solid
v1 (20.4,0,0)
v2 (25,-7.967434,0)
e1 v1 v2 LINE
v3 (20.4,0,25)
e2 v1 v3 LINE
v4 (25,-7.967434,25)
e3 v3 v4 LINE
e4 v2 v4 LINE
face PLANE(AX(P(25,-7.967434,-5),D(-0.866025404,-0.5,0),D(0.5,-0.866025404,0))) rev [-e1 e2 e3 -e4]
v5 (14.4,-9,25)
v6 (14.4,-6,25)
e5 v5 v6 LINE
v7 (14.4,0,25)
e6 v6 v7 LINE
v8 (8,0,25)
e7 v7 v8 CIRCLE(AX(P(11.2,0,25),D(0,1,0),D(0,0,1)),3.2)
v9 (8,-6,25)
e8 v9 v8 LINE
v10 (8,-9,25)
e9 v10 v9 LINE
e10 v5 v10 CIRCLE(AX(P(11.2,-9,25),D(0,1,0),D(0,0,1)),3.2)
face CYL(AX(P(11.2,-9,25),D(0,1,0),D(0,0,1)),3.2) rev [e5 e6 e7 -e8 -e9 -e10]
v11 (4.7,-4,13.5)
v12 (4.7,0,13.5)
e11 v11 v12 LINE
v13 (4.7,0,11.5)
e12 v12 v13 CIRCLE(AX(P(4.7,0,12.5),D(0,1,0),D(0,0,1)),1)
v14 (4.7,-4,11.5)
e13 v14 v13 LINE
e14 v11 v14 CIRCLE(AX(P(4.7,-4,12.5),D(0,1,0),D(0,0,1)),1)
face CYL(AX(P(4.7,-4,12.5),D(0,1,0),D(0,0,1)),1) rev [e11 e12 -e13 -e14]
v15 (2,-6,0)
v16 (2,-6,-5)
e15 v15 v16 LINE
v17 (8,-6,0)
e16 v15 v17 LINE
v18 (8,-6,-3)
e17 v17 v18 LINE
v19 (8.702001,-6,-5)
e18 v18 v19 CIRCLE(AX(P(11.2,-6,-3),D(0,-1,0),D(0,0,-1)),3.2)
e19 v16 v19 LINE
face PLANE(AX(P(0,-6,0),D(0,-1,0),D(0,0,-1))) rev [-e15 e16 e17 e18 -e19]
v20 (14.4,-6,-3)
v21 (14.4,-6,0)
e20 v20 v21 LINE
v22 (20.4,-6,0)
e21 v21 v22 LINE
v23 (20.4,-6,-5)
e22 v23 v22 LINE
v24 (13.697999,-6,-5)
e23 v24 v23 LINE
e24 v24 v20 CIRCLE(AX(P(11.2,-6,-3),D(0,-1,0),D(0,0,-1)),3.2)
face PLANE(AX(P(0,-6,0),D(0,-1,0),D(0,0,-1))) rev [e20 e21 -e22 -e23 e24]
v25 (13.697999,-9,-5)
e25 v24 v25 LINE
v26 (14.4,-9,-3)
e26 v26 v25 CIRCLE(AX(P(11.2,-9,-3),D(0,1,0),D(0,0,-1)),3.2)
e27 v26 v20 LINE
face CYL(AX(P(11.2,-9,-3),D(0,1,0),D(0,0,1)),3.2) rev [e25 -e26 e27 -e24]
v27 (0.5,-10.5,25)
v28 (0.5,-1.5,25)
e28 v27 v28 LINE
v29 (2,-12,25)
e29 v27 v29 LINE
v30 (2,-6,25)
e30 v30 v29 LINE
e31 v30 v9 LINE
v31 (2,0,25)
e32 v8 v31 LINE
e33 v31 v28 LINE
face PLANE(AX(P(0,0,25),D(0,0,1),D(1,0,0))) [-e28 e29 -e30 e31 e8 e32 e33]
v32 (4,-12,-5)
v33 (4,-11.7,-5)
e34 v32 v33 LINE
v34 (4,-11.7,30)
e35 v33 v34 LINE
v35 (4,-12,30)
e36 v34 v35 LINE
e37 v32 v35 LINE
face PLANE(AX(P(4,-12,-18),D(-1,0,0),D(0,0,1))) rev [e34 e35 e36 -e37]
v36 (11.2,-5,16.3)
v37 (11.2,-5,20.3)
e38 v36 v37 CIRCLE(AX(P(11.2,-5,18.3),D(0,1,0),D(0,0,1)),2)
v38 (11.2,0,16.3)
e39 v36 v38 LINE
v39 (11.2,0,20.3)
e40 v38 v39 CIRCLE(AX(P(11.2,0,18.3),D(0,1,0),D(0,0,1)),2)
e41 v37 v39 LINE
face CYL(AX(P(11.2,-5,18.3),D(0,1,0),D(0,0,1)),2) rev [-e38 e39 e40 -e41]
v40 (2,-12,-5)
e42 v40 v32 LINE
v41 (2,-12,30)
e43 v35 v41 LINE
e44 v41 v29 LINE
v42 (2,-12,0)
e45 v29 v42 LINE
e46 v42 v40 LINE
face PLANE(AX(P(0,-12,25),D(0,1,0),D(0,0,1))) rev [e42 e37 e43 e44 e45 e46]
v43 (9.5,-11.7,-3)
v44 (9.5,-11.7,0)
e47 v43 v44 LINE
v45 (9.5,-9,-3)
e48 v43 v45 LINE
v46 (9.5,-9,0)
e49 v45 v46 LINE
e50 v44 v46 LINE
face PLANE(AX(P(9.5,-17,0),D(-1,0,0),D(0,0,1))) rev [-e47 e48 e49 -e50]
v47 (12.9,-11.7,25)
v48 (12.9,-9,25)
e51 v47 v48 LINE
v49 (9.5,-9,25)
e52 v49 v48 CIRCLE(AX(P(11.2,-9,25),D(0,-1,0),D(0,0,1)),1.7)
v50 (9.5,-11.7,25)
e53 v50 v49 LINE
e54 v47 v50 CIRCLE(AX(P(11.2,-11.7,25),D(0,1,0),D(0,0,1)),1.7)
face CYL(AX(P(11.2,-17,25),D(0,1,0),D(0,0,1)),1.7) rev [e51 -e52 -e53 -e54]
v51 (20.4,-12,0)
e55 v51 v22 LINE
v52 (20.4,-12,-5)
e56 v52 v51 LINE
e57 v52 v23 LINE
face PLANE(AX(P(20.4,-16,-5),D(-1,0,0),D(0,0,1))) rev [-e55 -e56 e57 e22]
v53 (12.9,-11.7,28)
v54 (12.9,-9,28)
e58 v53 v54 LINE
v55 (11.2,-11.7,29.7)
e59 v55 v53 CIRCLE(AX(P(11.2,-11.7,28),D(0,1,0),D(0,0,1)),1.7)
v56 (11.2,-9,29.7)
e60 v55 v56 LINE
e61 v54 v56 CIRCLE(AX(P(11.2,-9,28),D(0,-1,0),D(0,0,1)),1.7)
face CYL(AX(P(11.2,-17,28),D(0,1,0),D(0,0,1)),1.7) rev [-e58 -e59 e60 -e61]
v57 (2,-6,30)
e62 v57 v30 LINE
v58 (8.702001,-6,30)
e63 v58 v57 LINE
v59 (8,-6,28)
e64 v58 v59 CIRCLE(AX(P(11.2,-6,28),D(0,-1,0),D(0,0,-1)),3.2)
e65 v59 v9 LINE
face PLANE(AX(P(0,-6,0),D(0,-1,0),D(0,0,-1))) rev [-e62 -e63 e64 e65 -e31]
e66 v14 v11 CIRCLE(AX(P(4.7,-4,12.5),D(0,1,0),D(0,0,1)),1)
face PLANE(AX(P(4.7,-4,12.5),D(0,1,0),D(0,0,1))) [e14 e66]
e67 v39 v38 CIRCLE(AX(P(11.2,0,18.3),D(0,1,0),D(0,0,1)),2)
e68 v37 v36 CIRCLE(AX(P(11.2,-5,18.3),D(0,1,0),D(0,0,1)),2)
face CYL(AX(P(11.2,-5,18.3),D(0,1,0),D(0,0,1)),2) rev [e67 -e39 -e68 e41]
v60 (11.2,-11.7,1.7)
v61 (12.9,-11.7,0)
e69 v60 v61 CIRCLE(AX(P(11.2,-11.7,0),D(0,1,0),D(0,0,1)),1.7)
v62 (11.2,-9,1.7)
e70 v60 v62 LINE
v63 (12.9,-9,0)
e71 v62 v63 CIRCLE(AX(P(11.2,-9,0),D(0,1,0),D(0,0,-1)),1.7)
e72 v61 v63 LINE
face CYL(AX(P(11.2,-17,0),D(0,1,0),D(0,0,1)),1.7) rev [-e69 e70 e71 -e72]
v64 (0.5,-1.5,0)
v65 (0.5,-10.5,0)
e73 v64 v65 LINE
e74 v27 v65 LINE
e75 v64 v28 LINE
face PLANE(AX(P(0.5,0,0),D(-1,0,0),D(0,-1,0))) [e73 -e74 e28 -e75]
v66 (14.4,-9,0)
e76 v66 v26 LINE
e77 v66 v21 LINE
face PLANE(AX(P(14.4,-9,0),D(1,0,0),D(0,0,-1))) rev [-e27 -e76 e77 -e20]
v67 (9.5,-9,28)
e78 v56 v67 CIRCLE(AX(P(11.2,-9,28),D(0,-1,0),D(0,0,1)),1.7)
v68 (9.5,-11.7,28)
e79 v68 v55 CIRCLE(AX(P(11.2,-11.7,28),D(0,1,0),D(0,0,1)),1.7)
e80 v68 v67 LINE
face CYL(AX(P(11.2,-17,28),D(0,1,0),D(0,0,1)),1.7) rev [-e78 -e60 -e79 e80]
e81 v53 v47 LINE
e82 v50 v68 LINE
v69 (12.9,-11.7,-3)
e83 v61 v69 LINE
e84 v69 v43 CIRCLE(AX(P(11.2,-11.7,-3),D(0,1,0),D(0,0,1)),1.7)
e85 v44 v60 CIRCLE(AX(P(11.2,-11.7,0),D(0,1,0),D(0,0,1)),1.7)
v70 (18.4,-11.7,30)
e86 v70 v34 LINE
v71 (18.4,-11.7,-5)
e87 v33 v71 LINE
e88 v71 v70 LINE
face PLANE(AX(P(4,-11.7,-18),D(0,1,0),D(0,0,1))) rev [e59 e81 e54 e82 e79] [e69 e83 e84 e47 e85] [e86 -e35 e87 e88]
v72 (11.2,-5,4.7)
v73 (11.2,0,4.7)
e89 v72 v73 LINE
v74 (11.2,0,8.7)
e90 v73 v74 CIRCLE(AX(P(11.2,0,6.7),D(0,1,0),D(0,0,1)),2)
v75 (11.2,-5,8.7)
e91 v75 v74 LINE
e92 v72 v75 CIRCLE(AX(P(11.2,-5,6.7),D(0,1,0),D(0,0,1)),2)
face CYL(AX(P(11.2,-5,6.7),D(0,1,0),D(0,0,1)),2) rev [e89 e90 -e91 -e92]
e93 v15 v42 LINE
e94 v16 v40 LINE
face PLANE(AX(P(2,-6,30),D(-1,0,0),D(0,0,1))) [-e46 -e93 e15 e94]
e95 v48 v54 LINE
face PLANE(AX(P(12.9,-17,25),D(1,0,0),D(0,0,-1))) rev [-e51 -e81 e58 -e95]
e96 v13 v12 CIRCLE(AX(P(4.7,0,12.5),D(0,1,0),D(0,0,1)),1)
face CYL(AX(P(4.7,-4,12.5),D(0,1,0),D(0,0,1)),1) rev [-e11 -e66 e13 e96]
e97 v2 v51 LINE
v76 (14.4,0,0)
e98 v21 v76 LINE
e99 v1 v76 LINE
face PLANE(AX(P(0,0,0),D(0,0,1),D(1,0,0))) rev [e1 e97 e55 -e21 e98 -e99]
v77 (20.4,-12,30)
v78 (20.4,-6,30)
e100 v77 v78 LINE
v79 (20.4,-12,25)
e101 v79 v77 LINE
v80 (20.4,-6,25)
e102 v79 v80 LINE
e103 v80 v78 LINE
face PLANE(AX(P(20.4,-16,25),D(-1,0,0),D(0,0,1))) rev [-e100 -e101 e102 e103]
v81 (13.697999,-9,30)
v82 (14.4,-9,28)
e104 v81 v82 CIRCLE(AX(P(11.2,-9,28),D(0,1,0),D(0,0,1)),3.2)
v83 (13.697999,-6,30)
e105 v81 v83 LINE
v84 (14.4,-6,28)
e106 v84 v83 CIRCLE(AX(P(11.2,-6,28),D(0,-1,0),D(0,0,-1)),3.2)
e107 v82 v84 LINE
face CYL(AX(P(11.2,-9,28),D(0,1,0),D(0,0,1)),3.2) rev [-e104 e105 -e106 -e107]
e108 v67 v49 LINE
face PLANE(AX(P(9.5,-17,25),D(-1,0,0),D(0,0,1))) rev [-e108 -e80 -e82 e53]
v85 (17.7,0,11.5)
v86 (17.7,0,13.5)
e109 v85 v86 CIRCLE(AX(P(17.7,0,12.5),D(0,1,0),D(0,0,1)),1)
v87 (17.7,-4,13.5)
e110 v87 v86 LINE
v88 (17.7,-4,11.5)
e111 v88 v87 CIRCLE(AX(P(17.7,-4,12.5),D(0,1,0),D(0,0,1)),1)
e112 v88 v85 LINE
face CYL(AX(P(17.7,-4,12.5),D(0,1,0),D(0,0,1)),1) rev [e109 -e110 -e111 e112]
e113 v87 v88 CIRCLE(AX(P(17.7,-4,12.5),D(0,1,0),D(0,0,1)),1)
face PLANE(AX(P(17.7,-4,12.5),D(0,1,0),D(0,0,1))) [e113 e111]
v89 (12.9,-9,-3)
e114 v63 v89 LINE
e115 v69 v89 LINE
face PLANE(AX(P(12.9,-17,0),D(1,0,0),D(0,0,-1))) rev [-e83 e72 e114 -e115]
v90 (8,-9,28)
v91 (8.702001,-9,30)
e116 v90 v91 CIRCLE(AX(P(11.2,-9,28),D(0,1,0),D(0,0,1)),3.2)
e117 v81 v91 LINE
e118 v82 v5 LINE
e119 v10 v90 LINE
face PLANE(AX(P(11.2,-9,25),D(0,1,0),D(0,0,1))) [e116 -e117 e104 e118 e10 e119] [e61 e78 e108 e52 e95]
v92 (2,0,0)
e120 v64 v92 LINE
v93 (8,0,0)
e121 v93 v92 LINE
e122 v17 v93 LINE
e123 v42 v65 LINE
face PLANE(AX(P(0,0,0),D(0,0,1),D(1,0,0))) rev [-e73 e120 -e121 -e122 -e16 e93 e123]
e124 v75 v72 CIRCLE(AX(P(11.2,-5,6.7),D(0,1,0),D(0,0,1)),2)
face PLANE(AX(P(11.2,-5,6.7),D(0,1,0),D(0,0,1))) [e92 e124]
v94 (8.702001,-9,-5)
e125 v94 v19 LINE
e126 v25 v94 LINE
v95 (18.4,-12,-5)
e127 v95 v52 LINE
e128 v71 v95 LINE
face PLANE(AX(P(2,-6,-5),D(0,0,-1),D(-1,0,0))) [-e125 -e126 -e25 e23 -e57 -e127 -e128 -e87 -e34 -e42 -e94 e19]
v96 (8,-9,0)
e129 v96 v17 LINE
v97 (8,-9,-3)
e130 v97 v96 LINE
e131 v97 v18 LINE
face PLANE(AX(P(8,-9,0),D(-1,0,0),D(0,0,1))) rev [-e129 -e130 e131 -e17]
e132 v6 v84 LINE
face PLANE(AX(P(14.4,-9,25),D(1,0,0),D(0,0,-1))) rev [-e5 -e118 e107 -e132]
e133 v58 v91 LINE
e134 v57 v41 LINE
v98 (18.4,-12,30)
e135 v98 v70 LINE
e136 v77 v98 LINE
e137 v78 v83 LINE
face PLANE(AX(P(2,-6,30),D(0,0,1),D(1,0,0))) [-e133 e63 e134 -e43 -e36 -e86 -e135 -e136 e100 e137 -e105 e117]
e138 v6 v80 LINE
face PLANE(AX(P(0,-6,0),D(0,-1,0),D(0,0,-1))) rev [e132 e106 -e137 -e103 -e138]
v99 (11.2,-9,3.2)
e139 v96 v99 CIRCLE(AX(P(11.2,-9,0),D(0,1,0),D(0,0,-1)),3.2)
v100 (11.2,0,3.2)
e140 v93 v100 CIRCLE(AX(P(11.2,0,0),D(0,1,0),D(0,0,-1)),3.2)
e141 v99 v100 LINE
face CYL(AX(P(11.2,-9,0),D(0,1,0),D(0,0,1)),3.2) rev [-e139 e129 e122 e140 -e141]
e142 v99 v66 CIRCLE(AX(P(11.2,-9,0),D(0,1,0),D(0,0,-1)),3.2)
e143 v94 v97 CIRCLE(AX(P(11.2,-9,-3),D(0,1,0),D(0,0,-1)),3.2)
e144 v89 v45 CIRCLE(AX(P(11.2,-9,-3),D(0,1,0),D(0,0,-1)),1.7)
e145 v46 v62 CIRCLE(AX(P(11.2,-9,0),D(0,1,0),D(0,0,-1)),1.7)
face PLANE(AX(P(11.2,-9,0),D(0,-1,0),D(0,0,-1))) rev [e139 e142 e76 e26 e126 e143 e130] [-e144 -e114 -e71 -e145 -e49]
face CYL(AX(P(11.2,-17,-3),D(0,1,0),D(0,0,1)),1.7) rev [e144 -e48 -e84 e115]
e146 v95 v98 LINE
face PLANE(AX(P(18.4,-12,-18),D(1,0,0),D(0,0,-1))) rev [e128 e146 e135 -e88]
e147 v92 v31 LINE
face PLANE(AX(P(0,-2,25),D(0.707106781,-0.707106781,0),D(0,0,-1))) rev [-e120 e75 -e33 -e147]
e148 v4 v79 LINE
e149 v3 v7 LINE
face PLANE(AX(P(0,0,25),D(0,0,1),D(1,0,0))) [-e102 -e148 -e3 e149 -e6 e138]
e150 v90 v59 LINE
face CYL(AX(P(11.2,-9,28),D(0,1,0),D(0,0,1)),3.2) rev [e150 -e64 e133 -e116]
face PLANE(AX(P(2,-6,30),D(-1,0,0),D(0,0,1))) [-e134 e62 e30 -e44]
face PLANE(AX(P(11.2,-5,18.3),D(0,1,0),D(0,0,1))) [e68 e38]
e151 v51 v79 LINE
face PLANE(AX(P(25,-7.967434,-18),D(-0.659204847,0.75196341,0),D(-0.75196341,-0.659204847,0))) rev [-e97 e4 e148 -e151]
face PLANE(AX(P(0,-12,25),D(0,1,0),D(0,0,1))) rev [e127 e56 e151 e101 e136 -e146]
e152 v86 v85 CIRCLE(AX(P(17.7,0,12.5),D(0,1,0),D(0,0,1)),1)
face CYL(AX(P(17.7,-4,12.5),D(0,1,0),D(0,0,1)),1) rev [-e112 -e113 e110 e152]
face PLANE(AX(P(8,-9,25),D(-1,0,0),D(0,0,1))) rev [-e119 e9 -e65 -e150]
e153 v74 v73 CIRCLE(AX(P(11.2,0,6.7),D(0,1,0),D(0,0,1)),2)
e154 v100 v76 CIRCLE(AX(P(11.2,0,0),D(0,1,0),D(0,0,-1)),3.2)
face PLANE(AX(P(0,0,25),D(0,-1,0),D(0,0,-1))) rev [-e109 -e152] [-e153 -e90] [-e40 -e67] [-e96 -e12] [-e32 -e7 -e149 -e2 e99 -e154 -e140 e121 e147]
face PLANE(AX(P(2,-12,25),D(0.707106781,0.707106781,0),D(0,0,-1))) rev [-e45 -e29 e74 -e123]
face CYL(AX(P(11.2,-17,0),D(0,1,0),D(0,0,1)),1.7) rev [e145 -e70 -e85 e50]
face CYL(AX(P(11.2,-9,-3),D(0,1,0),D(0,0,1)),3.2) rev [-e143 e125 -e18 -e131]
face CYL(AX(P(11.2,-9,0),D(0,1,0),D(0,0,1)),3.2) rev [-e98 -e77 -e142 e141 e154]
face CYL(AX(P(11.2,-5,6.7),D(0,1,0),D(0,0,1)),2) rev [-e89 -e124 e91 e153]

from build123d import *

# Parameters (mm, degrees)
SKETCH1_W           = 25
SKETCH1_H           = 12
BOSS_EXTRUDE1_DEPTH = 25
CUT_EXTRUDE1_DEPTH  = 30
CHAMFER1_SIZE       = 2
SKETCH5_W           = 21
SKETCH5_H           = 35
BOSS_EXTRUDE2_DEPTH = 6
SKETCH6_W           = 2.6
SKETCH6_H           = 5
CUT_EXTRUDE2_DEPTH  = 10
SKETCH11_W          = 14.4
SKETCH11_H          = 0.3
CUT_EXTRUDE5_DEPTH  = 48
CUT_EXTRUDE6_DEPTH  = 48
SKETCH15_W          = 25
SKETCH15_H          = 12
CUT_EXTRUDE8_DEPTH  = 0.5
SKETCH17_R          = 2
CUT_EXTRUDE10_DEPTH = 5
SKETCH18_R          = 1
CUT_EXTRUDE11_DEPTH = 4
CUT_EXTRUDE12_DEPTH = 17
CUT_EXTRUDE13_DEPTH = 9


with BuildPart() as part:
    # Sketch1 → Boss-Extrude1 (new body)
    with BuildSketch(Plane.XY):
        with Locations((12.5, -6)):
            Rectangle(SKETCH1_W, SKETCH1_H)
    extrude(amount=BOSS_EXTRUDE1_DEPTH)

    # Sketch2 → Cut-Extrude1 (cut)
    with BuildSketch(Plane.XY.offset(25)):
        Polygon((25, 0), (25, -7.967433715), (20.4, 0), align=None)
    extrude(amount=-CUT_EXTRUDE1_DEPTH, mode=Mode.SUBTRACT)

    # Chamfer1
    chamfer1_edges = [part.edges().sort_by_distance(p)[0] for p in [
        (0, 0, 12.5),
        (25, -12, 12.5),
        (0, -12, 12.5),
    ]]
    chamfer(chamfer1_edges, length=CHAMFER1_SIZE)

    # Sketch5 → Boss-Extrude2 (add)
    with BuildSketch(Plane.XZ.offset(12)):
        with Locations((12.5, 12.5)):
            Rectangle(SKETCH5_W, SKETCH5_H)
    extrude(amount=-BOSS_EXTRUDE2_DEPTH)

    # Sketch6 → Cut-Extrude2 (cut)
    with BuildSketch(Plane(origin=(0, -6, 0), x_dir=(1, 0, 0), z_dir=(0, 1, 0))):
        with Locations((21.7, -27.5)):
            Rectangle(SKETCH6_W, SKETCH6_H)
        with Locations((21.7, 2.5)):
            Rectangle(SKETCH6_W, SKETCH6_H)
    extrude(amount=-CUT_EXTRUDE2_DEPTH, mode=Mode.SUBTRACT)

    # Sketch11 → Cut-Extrude5 (cut)
    with BuildSketch(Plane.XY.offset(30)):
        with Locations((11.2, -11.85)):
            Rectangle(SKETCH11_W, SKETCH11_H)
    extrude(amount=-CUT_EXTRUDE5_DEPTH, mode=Mode.SUBTRACT)

    # Sketch12 → Cut-Extrude6 (cut)
    with BuildSketch(Plane.XY.offset(30)):
        Polygon((25, -7.967433715), (20.4, -12), (25.592855108, -12), align=None)
    extrude(amount=-CUT_EXTRUDE6_DEPTH, mode=Mode.SUBTRACT)

    # Sketch15 → Cut-Extrude8 (cut)
    with BuildSketch(Plane.ZY):
        with Locations((12.5, -6)):
            Rectangle(SKETCH15_W, SKETCH15_H)
    extrude(amount=-CUT_EXTRUDE8_DEPTH, mode=Mode.SUBTRACT)

    # Sketch17 → Cut-Extrude10 (cut)
    with BuildSketch(Plane(origin=(0, 0, 0), x_dir=(1, 0, 0), z_dir=(0, 1, 0))):
        with Locations(Location((11.2, -6.7, 0), (0, 0, 270))):
            Circle(SKETCH17_R)
        with Locations(Location((11.2, -18.3, 0), (0, 0, 270))):
            Circle(SKETCH17_R)
    extrude(amount=-CUT_EXTRUDE10_DEPTH, mode=Mode.SUBTRACT)

    # Sketch18 → Cut-Extrude11 (cut)
    with BuildSketch(Plane(origin=(0, 0, 0), x_dir=(1, 0, 0), z_dir=(0, 1, 0))):
        with Locations(Location((4.7, -12.5, 0), (0, 0, 270))):
            Circle(SKETCH18_R)
        with Locations(Location((17.7, -12.5, 0), (0, 0, 270))):
            Circle(SKETCH18_R)
    extrude(amount=-CUT_EXTRUDE11_DEPTH, mode=Mode.SUBTRACT)

    # Sketch19 → Cut-Extrude12 (cut)
    with BuildSketch(Plane(origin=(0, 0, 0), x_dir=(1, 0, 0), z_dir=(0, 1, 0))):
        with BuildLine():
            Line((12.9, -25), (12.9, -28))
            ThreePointArc((12.9, -28), (11.2, -29.7), (9.5, -28))
            Line((9.5, -28), (9.5, -25))
            ThreePointArc((9.5, -25), (11.2, -23.3), (12.9, -25))
        make_face()
        with BuildLine():
            Line((12.9, 0), (12.9, 3))
            ThreePointArc((12.9, 3), (11.2, 4.7), (9.5, 3))
            Line((9.5, 3), (9.5, 0))
            ThreePointArc((9.5, 0), (11.2, -1.7), (12.9, 0))
        make_face()
    extrude(amount=-CUT_EXTRUDE12_DEPTH, mode=Mode.SUBTRACT)

    # Sketch20 → Cut-Extrude13 (cut)
    with BuildSketch(Plane(origin=(0, 0, 0), x_dir=(1, 0, 0), z_dir=(0, 1, 0))):
        with BuildLine():
            Line((14.4, -25), (14.4, -28))
            ThreePointArc((14.4, -28), (11.2, -31.2), (8, -28))
            Line((8, -28), (8, -25))
            ThreePointArc((8, -25), (11.2, -21.8), (14.4, -25))
        make_face()
        with BuildLine():
            Line((14.4, 0), (14.4, 3))
            ThreePointArc((14.4, 3), (11.2, 6.2), (8, 3))
            Line((8, 3), (8, 0))
            ThreePointArc((8, 0), (11.2, -3.2), (14.4, 0))
        make_face()
    extrude(amount=-CUT_EXTRUDE13_DEPTH, mode=Mode.SUBTRACT)


solid = part.part
